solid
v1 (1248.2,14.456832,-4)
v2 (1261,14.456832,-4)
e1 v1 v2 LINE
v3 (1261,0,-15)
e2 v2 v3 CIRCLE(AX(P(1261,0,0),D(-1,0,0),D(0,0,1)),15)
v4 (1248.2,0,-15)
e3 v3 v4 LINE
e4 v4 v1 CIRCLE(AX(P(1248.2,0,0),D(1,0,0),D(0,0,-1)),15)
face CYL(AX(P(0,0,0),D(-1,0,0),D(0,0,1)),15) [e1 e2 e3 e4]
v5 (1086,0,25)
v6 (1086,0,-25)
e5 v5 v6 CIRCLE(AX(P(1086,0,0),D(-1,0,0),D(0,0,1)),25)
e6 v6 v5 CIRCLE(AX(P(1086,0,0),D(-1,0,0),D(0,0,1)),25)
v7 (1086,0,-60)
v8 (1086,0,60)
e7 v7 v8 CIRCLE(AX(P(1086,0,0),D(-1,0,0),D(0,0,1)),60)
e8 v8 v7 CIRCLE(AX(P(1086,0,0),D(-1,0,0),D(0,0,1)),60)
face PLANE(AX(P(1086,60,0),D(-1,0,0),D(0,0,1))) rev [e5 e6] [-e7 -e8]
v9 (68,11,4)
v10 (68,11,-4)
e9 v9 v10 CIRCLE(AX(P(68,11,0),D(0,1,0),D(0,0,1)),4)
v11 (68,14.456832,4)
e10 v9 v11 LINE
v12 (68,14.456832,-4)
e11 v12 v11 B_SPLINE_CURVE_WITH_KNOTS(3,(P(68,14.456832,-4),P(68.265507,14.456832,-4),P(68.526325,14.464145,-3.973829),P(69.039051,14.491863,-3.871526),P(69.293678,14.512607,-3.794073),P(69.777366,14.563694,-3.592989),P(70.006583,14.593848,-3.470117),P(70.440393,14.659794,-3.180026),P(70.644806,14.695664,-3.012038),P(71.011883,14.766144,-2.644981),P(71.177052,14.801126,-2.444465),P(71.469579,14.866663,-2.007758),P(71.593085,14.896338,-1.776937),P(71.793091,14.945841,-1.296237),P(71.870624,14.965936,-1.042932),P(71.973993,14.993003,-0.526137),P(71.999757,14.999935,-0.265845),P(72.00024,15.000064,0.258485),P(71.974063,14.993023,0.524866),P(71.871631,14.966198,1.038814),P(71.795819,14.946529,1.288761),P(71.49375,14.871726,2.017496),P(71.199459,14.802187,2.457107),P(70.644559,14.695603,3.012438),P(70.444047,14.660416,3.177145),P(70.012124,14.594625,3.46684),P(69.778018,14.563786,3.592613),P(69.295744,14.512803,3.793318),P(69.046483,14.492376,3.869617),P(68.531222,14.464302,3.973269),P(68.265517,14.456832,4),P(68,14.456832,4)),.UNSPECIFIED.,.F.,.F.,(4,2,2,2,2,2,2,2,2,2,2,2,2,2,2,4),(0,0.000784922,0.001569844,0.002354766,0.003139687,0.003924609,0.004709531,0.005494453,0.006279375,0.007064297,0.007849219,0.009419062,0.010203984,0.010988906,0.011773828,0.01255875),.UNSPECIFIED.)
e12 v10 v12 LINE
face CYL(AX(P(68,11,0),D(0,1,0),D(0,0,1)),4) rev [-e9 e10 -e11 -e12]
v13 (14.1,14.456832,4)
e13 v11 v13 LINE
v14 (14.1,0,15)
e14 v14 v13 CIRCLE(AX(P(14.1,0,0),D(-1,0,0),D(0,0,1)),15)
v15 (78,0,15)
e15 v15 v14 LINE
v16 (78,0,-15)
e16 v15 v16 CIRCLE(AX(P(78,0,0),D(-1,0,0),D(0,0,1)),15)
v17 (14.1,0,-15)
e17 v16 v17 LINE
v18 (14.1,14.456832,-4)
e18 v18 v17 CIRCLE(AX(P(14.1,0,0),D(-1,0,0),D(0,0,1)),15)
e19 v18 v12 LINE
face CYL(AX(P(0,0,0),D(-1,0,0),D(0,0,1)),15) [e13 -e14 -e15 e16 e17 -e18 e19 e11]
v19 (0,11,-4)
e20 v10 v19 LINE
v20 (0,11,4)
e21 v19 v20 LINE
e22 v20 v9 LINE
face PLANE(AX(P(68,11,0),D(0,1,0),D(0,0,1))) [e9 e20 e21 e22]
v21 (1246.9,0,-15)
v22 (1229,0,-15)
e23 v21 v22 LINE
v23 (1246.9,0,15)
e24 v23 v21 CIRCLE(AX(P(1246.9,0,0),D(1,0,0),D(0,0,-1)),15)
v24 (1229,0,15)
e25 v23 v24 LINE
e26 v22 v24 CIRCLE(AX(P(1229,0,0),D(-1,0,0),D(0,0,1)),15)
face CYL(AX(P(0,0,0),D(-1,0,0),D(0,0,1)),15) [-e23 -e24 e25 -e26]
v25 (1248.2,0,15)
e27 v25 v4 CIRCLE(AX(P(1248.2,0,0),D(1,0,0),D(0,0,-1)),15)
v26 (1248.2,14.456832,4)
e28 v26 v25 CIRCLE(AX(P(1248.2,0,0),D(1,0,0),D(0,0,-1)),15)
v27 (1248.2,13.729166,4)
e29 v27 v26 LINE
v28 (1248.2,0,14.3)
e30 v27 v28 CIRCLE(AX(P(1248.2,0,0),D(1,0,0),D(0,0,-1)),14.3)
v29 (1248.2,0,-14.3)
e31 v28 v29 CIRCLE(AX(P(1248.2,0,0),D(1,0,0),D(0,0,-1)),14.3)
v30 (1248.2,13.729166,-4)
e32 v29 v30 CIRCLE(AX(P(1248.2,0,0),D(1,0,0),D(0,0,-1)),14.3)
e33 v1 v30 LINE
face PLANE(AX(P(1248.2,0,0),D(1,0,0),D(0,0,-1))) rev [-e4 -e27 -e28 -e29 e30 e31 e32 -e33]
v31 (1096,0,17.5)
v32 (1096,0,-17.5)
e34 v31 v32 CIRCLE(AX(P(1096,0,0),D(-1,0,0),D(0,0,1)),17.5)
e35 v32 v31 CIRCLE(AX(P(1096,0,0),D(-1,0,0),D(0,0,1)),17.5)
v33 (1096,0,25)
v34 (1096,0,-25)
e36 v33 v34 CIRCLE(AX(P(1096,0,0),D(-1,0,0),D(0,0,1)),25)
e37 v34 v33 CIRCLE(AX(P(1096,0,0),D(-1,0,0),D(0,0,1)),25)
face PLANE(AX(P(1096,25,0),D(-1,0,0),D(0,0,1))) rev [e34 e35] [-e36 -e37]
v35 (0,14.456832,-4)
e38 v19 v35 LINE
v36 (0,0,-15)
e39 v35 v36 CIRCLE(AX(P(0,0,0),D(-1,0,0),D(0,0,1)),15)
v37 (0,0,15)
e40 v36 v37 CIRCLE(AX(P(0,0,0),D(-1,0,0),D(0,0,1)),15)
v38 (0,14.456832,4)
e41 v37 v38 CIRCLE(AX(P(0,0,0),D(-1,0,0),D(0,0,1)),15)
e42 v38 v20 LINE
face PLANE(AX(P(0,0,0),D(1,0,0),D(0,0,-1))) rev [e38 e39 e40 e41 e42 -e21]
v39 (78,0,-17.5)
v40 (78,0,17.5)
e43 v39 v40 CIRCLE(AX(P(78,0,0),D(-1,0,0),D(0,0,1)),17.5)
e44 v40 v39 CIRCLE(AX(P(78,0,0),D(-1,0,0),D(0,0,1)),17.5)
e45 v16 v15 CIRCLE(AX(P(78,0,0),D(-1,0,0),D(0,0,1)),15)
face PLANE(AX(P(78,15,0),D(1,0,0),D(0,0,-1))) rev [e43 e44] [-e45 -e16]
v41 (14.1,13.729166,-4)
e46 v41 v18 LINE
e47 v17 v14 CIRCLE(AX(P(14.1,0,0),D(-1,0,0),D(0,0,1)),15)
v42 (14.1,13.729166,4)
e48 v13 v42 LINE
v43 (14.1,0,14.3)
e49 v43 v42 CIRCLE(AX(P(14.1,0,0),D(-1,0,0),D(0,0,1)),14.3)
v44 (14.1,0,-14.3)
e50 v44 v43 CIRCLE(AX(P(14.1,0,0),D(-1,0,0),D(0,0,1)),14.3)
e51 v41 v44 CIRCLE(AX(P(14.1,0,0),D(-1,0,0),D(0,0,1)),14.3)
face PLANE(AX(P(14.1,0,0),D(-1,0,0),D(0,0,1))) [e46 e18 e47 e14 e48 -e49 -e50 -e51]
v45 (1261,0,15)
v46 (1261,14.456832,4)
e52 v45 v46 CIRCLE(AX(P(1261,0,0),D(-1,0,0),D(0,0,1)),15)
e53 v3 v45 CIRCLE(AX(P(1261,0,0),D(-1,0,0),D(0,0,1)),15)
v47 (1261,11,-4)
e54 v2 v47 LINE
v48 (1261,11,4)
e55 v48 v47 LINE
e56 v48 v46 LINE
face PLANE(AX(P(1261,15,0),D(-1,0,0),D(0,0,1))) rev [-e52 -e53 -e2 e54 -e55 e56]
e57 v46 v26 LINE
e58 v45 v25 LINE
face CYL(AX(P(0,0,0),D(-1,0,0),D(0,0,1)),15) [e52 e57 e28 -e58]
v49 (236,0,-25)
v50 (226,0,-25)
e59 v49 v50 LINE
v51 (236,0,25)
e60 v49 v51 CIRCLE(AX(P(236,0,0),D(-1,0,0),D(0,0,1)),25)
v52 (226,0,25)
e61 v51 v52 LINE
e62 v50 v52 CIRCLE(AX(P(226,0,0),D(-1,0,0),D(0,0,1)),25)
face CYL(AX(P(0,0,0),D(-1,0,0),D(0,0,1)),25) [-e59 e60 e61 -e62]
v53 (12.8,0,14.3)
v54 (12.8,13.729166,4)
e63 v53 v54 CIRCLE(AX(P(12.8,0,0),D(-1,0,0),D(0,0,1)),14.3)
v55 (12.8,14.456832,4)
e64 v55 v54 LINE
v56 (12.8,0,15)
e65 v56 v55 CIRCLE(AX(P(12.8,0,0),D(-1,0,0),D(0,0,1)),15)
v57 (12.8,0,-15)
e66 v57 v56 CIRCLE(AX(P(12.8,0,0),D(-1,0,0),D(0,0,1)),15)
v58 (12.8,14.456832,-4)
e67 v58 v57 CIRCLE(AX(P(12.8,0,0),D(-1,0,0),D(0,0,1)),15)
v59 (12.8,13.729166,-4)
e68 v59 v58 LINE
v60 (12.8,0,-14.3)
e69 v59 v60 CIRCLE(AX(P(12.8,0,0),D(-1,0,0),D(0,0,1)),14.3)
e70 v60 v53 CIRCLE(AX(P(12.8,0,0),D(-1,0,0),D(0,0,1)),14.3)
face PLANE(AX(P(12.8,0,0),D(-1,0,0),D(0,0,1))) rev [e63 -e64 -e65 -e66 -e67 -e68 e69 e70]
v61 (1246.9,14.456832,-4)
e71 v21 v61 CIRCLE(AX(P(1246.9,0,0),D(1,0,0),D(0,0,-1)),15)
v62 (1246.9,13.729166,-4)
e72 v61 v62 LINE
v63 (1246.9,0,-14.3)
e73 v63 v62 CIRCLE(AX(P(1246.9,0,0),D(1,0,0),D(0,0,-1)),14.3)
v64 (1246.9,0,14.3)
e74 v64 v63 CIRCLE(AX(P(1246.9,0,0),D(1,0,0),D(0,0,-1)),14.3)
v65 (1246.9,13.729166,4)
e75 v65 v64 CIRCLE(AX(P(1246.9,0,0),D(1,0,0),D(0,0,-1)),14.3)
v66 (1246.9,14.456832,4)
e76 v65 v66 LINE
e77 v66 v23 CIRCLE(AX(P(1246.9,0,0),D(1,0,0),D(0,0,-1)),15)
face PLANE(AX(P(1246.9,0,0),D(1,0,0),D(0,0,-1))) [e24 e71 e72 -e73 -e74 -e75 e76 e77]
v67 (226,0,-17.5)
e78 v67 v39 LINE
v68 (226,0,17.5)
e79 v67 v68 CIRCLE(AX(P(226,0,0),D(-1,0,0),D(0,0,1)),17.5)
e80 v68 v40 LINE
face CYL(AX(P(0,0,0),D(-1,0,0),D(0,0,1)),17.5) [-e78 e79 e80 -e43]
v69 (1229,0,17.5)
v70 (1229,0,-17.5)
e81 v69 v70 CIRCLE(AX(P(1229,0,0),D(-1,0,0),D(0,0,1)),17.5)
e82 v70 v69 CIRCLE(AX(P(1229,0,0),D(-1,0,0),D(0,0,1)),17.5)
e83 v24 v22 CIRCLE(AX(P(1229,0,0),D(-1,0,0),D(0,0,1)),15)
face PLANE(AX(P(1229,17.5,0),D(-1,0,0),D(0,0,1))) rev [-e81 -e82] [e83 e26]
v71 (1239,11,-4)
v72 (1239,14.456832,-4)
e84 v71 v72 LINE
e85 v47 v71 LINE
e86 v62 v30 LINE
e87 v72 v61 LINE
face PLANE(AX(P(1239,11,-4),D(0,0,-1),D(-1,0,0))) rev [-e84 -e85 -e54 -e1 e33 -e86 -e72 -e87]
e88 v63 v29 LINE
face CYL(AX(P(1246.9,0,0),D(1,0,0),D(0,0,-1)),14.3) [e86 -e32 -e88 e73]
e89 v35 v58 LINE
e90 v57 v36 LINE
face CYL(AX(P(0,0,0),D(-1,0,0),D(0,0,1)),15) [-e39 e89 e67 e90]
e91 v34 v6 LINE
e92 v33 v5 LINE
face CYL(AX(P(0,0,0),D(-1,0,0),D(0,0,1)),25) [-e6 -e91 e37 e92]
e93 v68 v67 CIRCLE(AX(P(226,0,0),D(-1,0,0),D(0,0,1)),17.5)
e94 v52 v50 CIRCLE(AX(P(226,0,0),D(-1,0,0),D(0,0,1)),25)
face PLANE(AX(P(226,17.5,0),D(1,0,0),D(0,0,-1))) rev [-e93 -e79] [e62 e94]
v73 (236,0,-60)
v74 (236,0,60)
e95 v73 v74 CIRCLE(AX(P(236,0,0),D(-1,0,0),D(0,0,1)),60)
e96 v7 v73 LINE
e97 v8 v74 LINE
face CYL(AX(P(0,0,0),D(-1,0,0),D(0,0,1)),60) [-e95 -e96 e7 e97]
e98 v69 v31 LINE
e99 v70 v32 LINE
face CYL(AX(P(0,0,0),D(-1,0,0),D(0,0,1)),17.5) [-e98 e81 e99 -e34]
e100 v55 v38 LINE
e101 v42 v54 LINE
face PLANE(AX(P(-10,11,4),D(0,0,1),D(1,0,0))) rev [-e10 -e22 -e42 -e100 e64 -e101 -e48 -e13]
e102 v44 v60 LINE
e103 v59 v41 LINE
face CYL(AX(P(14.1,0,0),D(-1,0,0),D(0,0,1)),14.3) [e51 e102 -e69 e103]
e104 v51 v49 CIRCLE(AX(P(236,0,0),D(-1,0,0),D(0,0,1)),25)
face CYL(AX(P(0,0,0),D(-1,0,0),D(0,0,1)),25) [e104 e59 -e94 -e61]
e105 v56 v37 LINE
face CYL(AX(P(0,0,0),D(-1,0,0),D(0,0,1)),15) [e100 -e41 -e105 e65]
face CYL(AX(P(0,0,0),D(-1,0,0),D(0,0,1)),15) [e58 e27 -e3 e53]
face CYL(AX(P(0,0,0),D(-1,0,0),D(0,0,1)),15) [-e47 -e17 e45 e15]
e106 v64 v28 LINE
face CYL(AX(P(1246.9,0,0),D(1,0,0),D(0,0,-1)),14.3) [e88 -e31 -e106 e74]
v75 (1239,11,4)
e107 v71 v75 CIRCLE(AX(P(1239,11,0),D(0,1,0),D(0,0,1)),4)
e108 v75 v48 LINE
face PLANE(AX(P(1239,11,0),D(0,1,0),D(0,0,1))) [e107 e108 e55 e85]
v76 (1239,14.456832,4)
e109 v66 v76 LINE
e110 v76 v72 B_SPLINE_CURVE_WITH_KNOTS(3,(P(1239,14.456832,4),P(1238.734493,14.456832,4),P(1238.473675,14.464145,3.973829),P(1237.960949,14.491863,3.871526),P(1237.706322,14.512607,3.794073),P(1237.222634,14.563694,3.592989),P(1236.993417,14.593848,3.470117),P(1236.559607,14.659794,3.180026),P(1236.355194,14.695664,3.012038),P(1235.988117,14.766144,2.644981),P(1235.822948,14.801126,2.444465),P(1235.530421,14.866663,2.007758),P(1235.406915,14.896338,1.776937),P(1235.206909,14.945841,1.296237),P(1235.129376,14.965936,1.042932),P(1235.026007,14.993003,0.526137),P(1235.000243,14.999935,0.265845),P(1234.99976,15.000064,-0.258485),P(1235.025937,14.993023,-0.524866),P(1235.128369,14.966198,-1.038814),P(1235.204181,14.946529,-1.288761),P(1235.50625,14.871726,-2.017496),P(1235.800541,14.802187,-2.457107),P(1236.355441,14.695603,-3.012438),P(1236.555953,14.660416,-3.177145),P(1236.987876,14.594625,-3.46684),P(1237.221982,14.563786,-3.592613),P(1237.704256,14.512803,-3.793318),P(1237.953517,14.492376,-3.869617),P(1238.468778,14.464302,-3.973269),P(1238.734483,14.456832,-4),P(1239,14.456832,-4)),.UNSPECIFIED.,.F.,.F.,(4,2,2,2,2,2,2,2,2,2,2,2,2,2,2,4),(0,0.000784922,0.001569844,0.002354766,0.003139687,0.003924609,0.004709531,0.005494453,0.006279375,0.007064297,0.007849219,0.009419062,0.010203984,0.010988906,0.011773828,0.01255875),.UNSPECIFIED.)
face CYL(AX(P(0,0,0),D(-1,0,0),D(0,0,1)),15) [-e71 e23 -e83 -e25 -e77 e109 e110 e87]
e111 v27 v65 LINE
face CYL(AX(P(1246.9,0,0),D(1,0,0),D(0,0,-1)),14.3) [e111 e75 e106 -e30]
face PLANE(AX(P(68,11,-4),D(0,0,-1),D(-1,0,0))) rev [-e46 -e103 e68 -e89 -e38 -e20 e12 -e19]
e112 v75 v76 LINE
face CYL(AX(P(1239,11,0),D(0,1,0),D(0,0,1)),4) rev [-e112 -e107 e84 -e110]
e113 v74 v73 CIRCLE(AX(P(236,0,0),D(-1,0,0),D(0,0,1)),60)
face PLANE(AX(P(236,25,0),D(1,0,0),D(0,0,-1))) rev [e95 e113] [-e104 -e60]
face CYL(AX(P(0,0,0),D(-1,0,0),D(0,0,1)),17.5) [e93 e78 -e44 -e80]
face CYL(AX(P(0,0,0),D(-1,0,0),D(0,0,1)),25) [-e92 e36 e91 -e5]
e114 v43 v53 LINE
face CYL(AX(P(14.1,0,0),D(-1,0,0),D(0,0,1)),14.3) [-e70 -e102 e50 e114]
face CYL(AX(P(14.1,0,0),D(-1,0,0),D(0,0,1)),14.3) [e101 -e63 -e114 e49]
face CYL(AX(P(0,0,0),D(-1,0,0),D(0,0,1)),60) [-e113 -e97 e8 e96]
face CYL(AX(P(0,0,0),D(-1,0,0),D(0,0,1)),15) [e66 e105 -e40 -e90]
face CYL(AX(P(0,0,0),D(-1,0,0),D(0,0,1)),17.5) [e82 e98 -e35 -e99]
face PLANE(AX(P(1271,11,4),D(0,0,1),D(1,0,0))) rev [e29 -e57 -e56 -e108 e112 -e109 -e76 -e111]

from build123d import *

# Parameters (mm, degrees)
CUT_EXTRUDE_1_DEPTH = 4
CUT_EXTRUDE_START   = -1.3
SKETCH_3_R          = 15
SKETCH_3_R_2        = 14.3
CUT_EXTRUDE_2_DEPTH = 1.3
CUT_EXTRUDE_3_DEPTH = 4
SKETCH_5_R          = 15
SKETCH_5_R_2        = 14.3
CUT_EXTRUDE_4_DEPTH = 1.3


with BuildPart() as part:
    # 草图1 → 旋转1 (revolve)
    with BuildSketch(Plane.XY, mode=Mode.PRIVATE) as revolve_1_sk:
        Polygon((0, 0), (0, 15), (78, 15), (78, 17.5), (226, 17.5), (226, 25), (236, 25), (236, 60), (1086, 60), (1086, 25), (1096, 25), (1096, 17.5), (1229, 17.5), (1229, 15), (1261, 15), (1261, 0), align=None)
    revolve(revolve_1_sk.sketch.rotate(Axis((0, 0, 0), (1, 0, 0)), 90), axis=Axis((0, 0, 0), (1, 0, 0)))

    # 草图2 → 切除-拉伸1 (cut)
    with BuildSketch(Plane(origin=(0, 15, 0), x_dir=(1, 0, 0), z_dir=(0, 1, 0))):
        with BuildLine():
            Line((68, 4), (-10, 4))
            Line((-10, 4), (-10, -4))
            Line((-10, -4), (68, -4))
            ThreePointArc((68, -4), (72, 0), (68, 4))
        make_face()
    extrude(amount=-CUT_EXTRUDE_1_DEPTH, mode=Mode.SUBTRACT)

    # 草图3 → 切除-拉伸2 (cut)
    with BuildSketch(Plane.ZY.offset(-12.8).offset(CUT_EXTRUDE_START)):
        Circle(SKETCH_3_R)
        Circle(SKETCH_3_R_2, mode=Mode.SUBTRACT)
    extrude(amount=CUT_EXTRUDE_2_DEPTH, mode=Mode.SUBTRACT)

    # 草图4 → 切除-拉伸3 (cut)
    with BuildSketch(Plane(origin=(0, 15, 0), x_dir=(1, 0, 0), z_dir=(0, 1, 0))):
        with BuildLine():
            Line((1239, 4), (1271, 4))
            Line((1271, 4), (1271, -4))
            Line((1271, -4), (1239, -4))
            ThreePointArc((1239, -4), (1235, 0), (1239, 4))
        make_face()
    extrude(amount=-CUT_EXTRUDE_3_DEPTH, mode=Mode.SUBTRACT)

    # 草图5 → 切除-拉伸4 (cut)
    with BuildSketch(Plane(origin=(1248.2, 0, 0), x_dir=(0, 0, -1), z_dir=(1, 0, 0))):
        with Locations(Location((0, 0, 0), (0, 0, 180))):
            Circle(SKETCH_5_R)
        Circle(SKETCH_5_R_2, mode=Mode.SUBTRACT)
    extrude(amount=-CUT_EXTRUDE_4_DEPTH, mode=Mode.SUBTRACT)


solid = part.part
